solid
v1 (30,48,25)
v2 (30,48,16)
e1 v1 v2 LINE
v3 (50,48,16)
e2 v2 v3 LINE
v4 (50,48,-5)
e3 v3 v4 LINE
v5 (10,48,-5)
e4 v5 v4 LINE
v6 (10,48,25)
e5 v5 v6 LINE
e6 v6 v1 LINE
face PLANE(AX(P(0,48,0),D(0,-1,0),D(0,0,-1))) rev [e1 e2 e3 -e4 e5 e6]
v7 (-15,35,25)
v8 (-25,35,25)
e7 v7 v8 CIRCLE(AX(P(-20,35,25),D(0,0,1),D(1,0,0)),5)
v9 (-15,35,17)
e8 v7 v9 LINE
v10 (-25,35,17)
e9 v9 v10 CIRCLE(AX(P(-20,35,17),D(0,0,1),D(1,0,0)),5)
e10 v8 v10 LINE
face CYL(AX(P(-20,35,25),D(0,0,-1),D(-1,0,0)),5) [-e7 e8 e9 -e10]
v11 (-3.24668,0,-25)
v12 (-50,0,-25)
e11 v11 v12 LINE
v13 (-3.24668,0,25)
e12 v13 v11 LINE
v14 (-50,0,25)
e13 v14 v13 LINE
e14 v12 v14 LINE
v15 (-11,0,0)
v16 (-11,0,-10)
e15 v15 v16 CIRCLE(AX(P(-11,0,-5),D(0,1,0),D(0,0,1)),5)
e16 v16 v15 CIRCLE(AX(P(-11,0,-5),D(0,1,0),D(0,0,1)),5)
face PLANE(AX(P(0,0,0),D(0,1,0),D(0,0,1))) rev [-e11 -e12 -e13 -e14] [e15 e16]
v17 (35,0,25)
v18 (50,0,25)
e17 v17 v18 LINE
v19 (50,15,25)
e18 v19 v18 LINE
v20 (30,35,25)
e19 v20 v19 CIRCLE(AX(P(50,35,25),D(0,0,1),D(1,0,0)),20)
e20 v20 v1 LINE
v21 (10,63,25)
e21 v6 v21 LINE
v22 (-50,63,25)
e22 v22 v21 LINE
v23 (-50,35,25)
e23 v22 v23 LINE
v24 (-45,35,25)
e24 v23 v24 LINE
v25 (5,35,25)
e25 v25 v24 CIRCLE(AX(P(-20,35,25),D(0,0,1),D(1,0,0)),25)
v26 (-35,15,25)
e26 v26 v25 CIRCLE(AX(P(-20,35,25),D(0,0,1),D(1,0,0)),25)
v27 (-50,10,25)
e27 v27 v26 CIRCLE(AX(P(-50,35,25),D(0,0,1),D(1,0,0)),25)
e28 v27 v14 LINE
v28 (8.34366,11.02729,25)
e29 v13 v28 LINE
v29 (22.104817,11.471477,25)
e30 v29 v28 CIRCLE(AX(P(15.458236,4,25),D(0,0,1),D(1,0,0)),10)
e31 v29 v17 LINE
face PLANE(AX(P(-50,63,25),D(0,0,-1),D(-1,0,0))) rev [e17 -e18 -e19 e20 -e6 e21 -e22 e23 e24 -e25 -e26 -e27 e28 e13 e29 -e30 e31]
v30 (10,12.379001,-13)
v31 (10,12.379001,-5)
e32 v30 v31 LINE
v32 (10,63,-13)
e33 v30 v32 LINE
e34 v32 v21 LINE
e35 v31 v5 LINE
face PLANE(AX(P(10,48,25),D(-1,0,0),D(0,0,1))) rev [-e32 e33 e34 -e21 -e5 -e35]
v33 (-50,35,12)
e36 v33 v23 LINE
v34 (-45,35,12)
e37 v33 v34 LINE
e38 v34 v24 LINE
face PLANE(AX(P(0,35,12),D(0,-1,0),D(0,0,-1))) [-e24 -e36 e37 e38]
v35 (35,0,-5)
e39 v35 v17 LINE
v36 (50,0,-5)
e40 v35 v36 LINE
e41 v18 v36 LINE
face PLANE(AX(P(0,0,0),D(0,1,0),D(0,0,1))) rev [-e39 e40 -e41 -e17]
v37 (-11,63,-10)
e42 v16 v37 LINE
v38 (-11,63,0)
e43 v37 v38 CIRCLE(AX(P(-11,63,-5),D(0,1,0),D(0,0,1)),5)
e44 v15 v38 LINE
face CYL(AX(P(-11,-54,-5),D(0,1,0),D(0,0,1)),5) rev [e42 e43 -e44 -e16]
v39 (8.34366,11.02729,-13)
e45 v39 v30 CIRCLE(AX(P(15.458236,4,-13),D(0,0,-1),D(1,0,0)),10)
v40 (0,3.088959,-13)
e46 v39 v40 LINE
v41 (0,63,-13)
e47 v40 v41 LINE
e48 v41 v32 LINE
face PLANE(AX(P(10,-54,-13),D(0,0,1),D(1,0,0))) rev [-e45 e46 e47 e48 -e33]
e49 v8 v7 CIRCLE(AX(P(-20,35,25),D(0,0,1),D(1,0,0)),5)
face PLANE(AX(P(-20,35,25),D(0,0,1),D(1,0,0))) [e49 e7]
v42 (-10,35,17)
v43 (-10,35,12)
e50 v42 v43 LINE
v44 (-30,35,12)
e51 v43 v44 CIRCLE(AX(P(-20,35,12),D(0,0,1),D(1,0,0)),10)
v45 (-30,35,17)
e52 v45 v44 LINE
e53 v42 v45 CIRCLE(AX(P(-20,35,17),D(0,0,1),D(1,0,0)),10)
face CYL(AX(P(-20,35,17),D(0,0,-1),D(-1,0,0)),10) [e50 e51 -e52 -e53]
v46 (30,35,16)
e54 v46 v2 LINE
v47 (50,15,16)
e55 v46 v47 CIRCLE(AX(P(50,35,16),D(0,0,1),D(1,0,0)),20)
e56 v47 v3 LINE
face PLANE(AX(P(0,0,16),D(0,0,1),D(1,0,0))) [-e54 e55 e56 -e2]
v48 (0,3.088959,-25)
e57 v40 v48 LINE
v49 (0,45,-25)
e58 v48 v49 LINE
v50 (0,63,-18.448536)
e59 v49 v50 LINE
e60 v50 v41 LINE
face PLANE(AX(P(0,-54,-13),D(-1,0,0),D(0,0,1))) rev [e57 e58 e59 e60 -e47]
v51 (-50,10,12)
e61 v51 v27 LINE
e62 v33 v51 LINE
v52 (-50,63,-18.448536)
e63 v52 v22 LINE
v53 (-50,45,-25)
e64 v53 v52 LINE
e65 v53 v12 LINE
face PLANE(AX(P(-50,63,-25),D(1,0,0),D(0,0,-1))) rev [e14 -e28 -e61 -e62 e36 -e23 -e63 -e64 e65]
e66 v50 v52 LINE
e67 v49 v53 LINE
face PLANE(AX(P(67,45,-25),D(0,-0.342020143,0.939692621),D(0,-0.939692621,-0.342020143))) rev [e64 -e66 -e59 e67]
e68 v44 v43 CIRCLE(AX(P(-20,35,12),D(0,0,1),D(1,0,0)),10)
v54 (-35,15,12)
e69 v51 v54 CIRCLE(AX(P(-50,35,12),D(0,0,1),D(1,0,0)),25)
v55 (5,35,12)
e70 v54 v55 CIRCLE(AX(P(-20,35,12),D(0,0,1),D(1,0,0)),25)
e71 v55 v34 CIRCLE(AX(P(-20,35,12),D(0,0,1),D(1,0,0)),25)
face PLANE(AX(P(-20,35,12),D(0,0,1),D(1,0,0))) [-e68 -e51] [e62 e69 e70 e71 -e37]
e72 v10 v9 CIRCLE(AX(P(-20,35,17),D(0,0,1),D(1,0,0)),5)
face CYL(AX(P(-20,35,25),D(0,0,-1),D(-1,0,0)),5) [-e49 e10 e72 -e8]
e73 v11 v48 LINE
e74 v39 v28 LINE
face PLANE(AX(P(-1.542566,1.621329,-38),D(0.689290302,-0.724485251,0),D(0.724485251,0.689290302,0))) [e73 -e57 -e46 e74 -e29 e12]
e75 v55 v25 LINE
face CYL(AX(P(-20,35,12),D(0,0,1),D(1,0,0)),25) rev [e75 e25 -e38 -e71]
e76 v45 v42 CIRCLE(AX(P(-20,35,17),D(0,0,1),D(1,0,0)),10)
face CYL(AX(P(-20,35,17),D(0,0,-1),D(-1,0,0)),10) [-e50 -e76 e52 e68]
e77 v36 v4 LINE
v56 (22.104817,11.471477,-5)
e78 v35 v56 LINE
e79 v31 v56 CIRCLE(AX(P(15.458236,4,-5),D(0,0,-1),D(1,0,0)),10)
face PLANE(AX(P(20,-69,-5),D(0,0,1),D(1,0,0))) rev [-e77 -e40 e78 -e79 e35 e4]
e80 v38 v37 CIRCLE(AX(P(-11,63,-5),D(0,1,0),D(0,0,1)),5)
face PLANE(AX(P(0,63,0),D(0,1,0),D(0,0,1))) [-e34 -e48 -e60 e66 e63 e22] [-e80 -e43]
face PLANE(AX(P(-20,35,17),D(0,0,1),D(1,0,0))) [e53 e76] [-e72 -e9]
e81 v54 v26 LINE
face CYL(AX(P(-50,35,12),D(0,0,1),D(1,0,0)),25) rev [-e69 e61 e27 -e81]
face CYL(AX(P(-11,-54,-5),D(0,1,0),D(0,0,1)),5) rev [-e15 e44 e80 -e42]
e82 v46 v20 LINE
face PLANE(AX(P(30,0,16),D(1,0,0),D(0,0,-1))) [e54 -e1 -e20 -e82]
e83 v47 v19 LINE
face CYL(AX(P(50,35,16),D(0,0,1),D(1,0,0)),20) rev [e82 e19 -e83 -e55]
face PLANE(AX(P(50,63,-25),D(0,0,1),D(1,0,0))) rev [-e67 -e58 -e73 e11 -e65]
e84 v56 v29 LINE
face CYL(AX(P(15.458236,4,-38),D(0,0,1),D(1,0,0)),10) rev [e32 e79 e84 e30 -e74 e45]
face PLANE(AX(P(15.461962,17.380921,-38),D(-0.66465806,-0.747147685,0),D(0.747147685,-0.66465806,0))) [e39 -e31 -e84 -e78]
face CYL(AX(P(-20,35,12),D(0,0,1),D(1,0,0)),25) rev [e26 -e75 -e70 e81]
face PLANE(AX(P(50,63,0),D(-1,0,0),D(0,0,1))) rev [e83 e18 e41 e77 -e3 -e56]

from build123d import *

# Parameters (mm, degrees)
BASE_BLOCK_DEPTH         = 63
CORNER_NOTCH_DEPTH       = 63
SIDE_POCKET_SKETCH_W     = 20
SIDE_POCKET_SKETCH_H     = 3.232862168
SIDE_POCKET_DEPTH        = 9
POCKET_SLOT_SKETCH_W     = 40
POCKET_SLOT_SKETCH_H     = 50
POCKET_SLOT_DEPTH        = 15
CIRCULAR_RECESS_SKETCH_R = 25
CIRCULAR_RECESS_DEPTH    = 13
PIN_BASE_20_SKETCH_R     = 10
PIN_BASE_20_DEPTH        = 5
PIN_10_SKETCH_R          = 5
PIN_10_DEPTH             = 8
RECESS_OPENING_DEPTH     = 13
THROUGH_SLOT_SKETCH_W    = 10
THROUGH_SLOT_SKETCH_H    = 12
THROUGH_SLOT_DEPTH       = 117
PROFILE_CUT_DEPTH        = 117
THROUGH_HOLE_10_SKETCH_R = 5
THROUGH_HOLE_10_DEPTH    = 117
CORNER_V_NOTCH_DEPTH     = 117


with BuildPart() as part:
    # Base Block Sketch → Base Block (new body)
    with BuildSketch(Plane(origin=(0, 0, 0), x_dir=(1, 0, 0), z_dir=(0, 1, 0))):
        Polygon((50, 0), (50, 25), (-50, 25), (-50, -25), (50, -25), align=None)
    extrude(amount=BASE_BLOCK_DEPTH)

    # Corner Notch Sketch → Corner Notch (cut)
    with BuildSketch(Plane.XY.offset(25)):
        with BuildLine():
            Line((35, 0), (22.104816934, 11.471476847))
            ThreePointArc((22.104816934, 11.471476847), (15.135621173, 13.994794618), (8.343659927, 11.027289849))
            Line((8.343659927, 11.027289849), (-3.246679913, 0))
            Line((-3.246679913, 0), (35, 0))
        make_face()
    extrude(amount=-CORNER_NOTCH_DEPTH, mode=Mode.SUBTRACT)

    # Side Pocket Sketch → Side Pocket (cut)
    with BuildSketch(Plane.XY.offset(25)):
        with BuildLine():
            ThreePointArc((30, 35), (35.857864376, 20.857864376), (50, 15))
            Line((50, 15), (50, 35))
            Line((50, 35), (50, 63))
            Line((50, 63), (30, 63))
            Line((30, 63), (30, 48))
            Line((30, 48), (30, 35))
        make_face()
        with Locations((40, 64.616431084)):
            Rectangle(SIDE_POCKET_SKETCH_W, SIDE_POCKET_SKETCH_H)
    extrude(amount=-SIDE_POCKET_DEPTH, mode=Mode.SUBTRACT)

    # Pocket Slot Sketch → Pocket Slot (cut)
    with BuildSketch(Plane(origin=(0, 63, 0), x_dir=(1, 0, 0), z_dir=(0, 1, 0))):
        with Locations((30, 0)):
            Rectangle(POCKET_SLOT_SKETCH_W, POCKET_SLOT_SKETCH_H)
    extrude(amount=-POCKET_SLOT_DEPTH, mode=Mode.SUBTRACT)

    # Circular Recess Sketch → Circular Recess (cut)
    with BuildSketch(Plane.XY.offset(25)):
        with Locations((-20, 35)):
            Circle(CIRCULAR_RECESS_SKETCH_R)
    extrude(amount=-CIRCULAR_RECESS_DEPTH, mode=Mode.SUBTRACT)

    # Pin Base Ø20 Sketch → Pin Base Ø20 (add)
    with BuildSketch(Plane.XY.offset(12)):
        with Locations((-20, 35)):
            Circle(PIN_BASE_20_SKETCH_R)
    extrude(amount=PIN_BASE_20_DEPTH)

    # Pin Ø10 Sketch → Pin Ø10 (add)
    with BuildSketch(Plane.XY.offset(17)):
        with Locations((-20, 35)):
            Circle(PIN_10_SKETCH_R)
    extrude(amount=PIN_10_DEPTH)

    # Recess Opening Sketch → Recess Opening (cut)
    with BuildSketch(Plane.XY.offset(25)):
        with BuildLine():
            Line((-45, 35), (-50, 35))
            Line((-50, 35), (-50, 10))
            ThreePointArc((-50, 10), (-42.09430585, 11.282917549), (-35, 15))
            ThreePointArc((-35, 15), (-42.360679775, 23.819660113), (-45, 35))
        make_face()
    extrude(amount=-RECESS_OPENING_DEPTH, mode=Mode.SUBTRACT)

    # Through Slot Sketch → Through Slot (cut)
    with BuildSketch(Plane(origin=(0, 63, 0), x_dir=(1, 0, 0), z_dir=(0, 1, 0))):
        with Locations((5, 19)):
            Rectangle(THROUGH_SLOT_SKETCH_W, THROUGH_SLOT_SKETCH_H)
    extrude(amount=-THROUGH_SLOT_DEPTH, mode=Mode.SUBTRACT)

    # Profile Cut Sketch → Profile Cut (cut)
    with BuildSketch(Plane(origin=(0, 48, 0), x_dir=(1, 0, 0), z_dir=(0, 1, 0))):
        Polygon((20, 5), (50, 5), (50, 25), (10, 25), (10, 5), align=None)
    extrude(amount=-PROFILE_CUT_DEPTH, mode=Mode.SUBTRACT)

    # Through Hole Ø10 Sketch → Through Hole Ø10 (cut)
    with BuildSketch(Plane(origin=(0, 63, 0), x_dir=(1, 0, 0), z_dir=(0, 1, 0))):
        with Locations(Location((-11, 5, 0), (0, 0, 270))):
            Circle(THROUGH_HOLE_10_SKETCH_R)
    extrude(amount=-THROUGH_HOLE_10_DEPTH, mode=Mode.SUBTRACT)

    # Corner V-Notch Sketch → Corner V-Notch (cut)
    with BuildSketch(Plane.ZY.offset(50)):
        Polygon((-25, 63), (-25, 45), (-18.448535783, 63), align=None)
    extrude(amount=-CORNER_V_NOTCH_DEPTH, mode=Mode.SUBTRACT)


solid = part.part
